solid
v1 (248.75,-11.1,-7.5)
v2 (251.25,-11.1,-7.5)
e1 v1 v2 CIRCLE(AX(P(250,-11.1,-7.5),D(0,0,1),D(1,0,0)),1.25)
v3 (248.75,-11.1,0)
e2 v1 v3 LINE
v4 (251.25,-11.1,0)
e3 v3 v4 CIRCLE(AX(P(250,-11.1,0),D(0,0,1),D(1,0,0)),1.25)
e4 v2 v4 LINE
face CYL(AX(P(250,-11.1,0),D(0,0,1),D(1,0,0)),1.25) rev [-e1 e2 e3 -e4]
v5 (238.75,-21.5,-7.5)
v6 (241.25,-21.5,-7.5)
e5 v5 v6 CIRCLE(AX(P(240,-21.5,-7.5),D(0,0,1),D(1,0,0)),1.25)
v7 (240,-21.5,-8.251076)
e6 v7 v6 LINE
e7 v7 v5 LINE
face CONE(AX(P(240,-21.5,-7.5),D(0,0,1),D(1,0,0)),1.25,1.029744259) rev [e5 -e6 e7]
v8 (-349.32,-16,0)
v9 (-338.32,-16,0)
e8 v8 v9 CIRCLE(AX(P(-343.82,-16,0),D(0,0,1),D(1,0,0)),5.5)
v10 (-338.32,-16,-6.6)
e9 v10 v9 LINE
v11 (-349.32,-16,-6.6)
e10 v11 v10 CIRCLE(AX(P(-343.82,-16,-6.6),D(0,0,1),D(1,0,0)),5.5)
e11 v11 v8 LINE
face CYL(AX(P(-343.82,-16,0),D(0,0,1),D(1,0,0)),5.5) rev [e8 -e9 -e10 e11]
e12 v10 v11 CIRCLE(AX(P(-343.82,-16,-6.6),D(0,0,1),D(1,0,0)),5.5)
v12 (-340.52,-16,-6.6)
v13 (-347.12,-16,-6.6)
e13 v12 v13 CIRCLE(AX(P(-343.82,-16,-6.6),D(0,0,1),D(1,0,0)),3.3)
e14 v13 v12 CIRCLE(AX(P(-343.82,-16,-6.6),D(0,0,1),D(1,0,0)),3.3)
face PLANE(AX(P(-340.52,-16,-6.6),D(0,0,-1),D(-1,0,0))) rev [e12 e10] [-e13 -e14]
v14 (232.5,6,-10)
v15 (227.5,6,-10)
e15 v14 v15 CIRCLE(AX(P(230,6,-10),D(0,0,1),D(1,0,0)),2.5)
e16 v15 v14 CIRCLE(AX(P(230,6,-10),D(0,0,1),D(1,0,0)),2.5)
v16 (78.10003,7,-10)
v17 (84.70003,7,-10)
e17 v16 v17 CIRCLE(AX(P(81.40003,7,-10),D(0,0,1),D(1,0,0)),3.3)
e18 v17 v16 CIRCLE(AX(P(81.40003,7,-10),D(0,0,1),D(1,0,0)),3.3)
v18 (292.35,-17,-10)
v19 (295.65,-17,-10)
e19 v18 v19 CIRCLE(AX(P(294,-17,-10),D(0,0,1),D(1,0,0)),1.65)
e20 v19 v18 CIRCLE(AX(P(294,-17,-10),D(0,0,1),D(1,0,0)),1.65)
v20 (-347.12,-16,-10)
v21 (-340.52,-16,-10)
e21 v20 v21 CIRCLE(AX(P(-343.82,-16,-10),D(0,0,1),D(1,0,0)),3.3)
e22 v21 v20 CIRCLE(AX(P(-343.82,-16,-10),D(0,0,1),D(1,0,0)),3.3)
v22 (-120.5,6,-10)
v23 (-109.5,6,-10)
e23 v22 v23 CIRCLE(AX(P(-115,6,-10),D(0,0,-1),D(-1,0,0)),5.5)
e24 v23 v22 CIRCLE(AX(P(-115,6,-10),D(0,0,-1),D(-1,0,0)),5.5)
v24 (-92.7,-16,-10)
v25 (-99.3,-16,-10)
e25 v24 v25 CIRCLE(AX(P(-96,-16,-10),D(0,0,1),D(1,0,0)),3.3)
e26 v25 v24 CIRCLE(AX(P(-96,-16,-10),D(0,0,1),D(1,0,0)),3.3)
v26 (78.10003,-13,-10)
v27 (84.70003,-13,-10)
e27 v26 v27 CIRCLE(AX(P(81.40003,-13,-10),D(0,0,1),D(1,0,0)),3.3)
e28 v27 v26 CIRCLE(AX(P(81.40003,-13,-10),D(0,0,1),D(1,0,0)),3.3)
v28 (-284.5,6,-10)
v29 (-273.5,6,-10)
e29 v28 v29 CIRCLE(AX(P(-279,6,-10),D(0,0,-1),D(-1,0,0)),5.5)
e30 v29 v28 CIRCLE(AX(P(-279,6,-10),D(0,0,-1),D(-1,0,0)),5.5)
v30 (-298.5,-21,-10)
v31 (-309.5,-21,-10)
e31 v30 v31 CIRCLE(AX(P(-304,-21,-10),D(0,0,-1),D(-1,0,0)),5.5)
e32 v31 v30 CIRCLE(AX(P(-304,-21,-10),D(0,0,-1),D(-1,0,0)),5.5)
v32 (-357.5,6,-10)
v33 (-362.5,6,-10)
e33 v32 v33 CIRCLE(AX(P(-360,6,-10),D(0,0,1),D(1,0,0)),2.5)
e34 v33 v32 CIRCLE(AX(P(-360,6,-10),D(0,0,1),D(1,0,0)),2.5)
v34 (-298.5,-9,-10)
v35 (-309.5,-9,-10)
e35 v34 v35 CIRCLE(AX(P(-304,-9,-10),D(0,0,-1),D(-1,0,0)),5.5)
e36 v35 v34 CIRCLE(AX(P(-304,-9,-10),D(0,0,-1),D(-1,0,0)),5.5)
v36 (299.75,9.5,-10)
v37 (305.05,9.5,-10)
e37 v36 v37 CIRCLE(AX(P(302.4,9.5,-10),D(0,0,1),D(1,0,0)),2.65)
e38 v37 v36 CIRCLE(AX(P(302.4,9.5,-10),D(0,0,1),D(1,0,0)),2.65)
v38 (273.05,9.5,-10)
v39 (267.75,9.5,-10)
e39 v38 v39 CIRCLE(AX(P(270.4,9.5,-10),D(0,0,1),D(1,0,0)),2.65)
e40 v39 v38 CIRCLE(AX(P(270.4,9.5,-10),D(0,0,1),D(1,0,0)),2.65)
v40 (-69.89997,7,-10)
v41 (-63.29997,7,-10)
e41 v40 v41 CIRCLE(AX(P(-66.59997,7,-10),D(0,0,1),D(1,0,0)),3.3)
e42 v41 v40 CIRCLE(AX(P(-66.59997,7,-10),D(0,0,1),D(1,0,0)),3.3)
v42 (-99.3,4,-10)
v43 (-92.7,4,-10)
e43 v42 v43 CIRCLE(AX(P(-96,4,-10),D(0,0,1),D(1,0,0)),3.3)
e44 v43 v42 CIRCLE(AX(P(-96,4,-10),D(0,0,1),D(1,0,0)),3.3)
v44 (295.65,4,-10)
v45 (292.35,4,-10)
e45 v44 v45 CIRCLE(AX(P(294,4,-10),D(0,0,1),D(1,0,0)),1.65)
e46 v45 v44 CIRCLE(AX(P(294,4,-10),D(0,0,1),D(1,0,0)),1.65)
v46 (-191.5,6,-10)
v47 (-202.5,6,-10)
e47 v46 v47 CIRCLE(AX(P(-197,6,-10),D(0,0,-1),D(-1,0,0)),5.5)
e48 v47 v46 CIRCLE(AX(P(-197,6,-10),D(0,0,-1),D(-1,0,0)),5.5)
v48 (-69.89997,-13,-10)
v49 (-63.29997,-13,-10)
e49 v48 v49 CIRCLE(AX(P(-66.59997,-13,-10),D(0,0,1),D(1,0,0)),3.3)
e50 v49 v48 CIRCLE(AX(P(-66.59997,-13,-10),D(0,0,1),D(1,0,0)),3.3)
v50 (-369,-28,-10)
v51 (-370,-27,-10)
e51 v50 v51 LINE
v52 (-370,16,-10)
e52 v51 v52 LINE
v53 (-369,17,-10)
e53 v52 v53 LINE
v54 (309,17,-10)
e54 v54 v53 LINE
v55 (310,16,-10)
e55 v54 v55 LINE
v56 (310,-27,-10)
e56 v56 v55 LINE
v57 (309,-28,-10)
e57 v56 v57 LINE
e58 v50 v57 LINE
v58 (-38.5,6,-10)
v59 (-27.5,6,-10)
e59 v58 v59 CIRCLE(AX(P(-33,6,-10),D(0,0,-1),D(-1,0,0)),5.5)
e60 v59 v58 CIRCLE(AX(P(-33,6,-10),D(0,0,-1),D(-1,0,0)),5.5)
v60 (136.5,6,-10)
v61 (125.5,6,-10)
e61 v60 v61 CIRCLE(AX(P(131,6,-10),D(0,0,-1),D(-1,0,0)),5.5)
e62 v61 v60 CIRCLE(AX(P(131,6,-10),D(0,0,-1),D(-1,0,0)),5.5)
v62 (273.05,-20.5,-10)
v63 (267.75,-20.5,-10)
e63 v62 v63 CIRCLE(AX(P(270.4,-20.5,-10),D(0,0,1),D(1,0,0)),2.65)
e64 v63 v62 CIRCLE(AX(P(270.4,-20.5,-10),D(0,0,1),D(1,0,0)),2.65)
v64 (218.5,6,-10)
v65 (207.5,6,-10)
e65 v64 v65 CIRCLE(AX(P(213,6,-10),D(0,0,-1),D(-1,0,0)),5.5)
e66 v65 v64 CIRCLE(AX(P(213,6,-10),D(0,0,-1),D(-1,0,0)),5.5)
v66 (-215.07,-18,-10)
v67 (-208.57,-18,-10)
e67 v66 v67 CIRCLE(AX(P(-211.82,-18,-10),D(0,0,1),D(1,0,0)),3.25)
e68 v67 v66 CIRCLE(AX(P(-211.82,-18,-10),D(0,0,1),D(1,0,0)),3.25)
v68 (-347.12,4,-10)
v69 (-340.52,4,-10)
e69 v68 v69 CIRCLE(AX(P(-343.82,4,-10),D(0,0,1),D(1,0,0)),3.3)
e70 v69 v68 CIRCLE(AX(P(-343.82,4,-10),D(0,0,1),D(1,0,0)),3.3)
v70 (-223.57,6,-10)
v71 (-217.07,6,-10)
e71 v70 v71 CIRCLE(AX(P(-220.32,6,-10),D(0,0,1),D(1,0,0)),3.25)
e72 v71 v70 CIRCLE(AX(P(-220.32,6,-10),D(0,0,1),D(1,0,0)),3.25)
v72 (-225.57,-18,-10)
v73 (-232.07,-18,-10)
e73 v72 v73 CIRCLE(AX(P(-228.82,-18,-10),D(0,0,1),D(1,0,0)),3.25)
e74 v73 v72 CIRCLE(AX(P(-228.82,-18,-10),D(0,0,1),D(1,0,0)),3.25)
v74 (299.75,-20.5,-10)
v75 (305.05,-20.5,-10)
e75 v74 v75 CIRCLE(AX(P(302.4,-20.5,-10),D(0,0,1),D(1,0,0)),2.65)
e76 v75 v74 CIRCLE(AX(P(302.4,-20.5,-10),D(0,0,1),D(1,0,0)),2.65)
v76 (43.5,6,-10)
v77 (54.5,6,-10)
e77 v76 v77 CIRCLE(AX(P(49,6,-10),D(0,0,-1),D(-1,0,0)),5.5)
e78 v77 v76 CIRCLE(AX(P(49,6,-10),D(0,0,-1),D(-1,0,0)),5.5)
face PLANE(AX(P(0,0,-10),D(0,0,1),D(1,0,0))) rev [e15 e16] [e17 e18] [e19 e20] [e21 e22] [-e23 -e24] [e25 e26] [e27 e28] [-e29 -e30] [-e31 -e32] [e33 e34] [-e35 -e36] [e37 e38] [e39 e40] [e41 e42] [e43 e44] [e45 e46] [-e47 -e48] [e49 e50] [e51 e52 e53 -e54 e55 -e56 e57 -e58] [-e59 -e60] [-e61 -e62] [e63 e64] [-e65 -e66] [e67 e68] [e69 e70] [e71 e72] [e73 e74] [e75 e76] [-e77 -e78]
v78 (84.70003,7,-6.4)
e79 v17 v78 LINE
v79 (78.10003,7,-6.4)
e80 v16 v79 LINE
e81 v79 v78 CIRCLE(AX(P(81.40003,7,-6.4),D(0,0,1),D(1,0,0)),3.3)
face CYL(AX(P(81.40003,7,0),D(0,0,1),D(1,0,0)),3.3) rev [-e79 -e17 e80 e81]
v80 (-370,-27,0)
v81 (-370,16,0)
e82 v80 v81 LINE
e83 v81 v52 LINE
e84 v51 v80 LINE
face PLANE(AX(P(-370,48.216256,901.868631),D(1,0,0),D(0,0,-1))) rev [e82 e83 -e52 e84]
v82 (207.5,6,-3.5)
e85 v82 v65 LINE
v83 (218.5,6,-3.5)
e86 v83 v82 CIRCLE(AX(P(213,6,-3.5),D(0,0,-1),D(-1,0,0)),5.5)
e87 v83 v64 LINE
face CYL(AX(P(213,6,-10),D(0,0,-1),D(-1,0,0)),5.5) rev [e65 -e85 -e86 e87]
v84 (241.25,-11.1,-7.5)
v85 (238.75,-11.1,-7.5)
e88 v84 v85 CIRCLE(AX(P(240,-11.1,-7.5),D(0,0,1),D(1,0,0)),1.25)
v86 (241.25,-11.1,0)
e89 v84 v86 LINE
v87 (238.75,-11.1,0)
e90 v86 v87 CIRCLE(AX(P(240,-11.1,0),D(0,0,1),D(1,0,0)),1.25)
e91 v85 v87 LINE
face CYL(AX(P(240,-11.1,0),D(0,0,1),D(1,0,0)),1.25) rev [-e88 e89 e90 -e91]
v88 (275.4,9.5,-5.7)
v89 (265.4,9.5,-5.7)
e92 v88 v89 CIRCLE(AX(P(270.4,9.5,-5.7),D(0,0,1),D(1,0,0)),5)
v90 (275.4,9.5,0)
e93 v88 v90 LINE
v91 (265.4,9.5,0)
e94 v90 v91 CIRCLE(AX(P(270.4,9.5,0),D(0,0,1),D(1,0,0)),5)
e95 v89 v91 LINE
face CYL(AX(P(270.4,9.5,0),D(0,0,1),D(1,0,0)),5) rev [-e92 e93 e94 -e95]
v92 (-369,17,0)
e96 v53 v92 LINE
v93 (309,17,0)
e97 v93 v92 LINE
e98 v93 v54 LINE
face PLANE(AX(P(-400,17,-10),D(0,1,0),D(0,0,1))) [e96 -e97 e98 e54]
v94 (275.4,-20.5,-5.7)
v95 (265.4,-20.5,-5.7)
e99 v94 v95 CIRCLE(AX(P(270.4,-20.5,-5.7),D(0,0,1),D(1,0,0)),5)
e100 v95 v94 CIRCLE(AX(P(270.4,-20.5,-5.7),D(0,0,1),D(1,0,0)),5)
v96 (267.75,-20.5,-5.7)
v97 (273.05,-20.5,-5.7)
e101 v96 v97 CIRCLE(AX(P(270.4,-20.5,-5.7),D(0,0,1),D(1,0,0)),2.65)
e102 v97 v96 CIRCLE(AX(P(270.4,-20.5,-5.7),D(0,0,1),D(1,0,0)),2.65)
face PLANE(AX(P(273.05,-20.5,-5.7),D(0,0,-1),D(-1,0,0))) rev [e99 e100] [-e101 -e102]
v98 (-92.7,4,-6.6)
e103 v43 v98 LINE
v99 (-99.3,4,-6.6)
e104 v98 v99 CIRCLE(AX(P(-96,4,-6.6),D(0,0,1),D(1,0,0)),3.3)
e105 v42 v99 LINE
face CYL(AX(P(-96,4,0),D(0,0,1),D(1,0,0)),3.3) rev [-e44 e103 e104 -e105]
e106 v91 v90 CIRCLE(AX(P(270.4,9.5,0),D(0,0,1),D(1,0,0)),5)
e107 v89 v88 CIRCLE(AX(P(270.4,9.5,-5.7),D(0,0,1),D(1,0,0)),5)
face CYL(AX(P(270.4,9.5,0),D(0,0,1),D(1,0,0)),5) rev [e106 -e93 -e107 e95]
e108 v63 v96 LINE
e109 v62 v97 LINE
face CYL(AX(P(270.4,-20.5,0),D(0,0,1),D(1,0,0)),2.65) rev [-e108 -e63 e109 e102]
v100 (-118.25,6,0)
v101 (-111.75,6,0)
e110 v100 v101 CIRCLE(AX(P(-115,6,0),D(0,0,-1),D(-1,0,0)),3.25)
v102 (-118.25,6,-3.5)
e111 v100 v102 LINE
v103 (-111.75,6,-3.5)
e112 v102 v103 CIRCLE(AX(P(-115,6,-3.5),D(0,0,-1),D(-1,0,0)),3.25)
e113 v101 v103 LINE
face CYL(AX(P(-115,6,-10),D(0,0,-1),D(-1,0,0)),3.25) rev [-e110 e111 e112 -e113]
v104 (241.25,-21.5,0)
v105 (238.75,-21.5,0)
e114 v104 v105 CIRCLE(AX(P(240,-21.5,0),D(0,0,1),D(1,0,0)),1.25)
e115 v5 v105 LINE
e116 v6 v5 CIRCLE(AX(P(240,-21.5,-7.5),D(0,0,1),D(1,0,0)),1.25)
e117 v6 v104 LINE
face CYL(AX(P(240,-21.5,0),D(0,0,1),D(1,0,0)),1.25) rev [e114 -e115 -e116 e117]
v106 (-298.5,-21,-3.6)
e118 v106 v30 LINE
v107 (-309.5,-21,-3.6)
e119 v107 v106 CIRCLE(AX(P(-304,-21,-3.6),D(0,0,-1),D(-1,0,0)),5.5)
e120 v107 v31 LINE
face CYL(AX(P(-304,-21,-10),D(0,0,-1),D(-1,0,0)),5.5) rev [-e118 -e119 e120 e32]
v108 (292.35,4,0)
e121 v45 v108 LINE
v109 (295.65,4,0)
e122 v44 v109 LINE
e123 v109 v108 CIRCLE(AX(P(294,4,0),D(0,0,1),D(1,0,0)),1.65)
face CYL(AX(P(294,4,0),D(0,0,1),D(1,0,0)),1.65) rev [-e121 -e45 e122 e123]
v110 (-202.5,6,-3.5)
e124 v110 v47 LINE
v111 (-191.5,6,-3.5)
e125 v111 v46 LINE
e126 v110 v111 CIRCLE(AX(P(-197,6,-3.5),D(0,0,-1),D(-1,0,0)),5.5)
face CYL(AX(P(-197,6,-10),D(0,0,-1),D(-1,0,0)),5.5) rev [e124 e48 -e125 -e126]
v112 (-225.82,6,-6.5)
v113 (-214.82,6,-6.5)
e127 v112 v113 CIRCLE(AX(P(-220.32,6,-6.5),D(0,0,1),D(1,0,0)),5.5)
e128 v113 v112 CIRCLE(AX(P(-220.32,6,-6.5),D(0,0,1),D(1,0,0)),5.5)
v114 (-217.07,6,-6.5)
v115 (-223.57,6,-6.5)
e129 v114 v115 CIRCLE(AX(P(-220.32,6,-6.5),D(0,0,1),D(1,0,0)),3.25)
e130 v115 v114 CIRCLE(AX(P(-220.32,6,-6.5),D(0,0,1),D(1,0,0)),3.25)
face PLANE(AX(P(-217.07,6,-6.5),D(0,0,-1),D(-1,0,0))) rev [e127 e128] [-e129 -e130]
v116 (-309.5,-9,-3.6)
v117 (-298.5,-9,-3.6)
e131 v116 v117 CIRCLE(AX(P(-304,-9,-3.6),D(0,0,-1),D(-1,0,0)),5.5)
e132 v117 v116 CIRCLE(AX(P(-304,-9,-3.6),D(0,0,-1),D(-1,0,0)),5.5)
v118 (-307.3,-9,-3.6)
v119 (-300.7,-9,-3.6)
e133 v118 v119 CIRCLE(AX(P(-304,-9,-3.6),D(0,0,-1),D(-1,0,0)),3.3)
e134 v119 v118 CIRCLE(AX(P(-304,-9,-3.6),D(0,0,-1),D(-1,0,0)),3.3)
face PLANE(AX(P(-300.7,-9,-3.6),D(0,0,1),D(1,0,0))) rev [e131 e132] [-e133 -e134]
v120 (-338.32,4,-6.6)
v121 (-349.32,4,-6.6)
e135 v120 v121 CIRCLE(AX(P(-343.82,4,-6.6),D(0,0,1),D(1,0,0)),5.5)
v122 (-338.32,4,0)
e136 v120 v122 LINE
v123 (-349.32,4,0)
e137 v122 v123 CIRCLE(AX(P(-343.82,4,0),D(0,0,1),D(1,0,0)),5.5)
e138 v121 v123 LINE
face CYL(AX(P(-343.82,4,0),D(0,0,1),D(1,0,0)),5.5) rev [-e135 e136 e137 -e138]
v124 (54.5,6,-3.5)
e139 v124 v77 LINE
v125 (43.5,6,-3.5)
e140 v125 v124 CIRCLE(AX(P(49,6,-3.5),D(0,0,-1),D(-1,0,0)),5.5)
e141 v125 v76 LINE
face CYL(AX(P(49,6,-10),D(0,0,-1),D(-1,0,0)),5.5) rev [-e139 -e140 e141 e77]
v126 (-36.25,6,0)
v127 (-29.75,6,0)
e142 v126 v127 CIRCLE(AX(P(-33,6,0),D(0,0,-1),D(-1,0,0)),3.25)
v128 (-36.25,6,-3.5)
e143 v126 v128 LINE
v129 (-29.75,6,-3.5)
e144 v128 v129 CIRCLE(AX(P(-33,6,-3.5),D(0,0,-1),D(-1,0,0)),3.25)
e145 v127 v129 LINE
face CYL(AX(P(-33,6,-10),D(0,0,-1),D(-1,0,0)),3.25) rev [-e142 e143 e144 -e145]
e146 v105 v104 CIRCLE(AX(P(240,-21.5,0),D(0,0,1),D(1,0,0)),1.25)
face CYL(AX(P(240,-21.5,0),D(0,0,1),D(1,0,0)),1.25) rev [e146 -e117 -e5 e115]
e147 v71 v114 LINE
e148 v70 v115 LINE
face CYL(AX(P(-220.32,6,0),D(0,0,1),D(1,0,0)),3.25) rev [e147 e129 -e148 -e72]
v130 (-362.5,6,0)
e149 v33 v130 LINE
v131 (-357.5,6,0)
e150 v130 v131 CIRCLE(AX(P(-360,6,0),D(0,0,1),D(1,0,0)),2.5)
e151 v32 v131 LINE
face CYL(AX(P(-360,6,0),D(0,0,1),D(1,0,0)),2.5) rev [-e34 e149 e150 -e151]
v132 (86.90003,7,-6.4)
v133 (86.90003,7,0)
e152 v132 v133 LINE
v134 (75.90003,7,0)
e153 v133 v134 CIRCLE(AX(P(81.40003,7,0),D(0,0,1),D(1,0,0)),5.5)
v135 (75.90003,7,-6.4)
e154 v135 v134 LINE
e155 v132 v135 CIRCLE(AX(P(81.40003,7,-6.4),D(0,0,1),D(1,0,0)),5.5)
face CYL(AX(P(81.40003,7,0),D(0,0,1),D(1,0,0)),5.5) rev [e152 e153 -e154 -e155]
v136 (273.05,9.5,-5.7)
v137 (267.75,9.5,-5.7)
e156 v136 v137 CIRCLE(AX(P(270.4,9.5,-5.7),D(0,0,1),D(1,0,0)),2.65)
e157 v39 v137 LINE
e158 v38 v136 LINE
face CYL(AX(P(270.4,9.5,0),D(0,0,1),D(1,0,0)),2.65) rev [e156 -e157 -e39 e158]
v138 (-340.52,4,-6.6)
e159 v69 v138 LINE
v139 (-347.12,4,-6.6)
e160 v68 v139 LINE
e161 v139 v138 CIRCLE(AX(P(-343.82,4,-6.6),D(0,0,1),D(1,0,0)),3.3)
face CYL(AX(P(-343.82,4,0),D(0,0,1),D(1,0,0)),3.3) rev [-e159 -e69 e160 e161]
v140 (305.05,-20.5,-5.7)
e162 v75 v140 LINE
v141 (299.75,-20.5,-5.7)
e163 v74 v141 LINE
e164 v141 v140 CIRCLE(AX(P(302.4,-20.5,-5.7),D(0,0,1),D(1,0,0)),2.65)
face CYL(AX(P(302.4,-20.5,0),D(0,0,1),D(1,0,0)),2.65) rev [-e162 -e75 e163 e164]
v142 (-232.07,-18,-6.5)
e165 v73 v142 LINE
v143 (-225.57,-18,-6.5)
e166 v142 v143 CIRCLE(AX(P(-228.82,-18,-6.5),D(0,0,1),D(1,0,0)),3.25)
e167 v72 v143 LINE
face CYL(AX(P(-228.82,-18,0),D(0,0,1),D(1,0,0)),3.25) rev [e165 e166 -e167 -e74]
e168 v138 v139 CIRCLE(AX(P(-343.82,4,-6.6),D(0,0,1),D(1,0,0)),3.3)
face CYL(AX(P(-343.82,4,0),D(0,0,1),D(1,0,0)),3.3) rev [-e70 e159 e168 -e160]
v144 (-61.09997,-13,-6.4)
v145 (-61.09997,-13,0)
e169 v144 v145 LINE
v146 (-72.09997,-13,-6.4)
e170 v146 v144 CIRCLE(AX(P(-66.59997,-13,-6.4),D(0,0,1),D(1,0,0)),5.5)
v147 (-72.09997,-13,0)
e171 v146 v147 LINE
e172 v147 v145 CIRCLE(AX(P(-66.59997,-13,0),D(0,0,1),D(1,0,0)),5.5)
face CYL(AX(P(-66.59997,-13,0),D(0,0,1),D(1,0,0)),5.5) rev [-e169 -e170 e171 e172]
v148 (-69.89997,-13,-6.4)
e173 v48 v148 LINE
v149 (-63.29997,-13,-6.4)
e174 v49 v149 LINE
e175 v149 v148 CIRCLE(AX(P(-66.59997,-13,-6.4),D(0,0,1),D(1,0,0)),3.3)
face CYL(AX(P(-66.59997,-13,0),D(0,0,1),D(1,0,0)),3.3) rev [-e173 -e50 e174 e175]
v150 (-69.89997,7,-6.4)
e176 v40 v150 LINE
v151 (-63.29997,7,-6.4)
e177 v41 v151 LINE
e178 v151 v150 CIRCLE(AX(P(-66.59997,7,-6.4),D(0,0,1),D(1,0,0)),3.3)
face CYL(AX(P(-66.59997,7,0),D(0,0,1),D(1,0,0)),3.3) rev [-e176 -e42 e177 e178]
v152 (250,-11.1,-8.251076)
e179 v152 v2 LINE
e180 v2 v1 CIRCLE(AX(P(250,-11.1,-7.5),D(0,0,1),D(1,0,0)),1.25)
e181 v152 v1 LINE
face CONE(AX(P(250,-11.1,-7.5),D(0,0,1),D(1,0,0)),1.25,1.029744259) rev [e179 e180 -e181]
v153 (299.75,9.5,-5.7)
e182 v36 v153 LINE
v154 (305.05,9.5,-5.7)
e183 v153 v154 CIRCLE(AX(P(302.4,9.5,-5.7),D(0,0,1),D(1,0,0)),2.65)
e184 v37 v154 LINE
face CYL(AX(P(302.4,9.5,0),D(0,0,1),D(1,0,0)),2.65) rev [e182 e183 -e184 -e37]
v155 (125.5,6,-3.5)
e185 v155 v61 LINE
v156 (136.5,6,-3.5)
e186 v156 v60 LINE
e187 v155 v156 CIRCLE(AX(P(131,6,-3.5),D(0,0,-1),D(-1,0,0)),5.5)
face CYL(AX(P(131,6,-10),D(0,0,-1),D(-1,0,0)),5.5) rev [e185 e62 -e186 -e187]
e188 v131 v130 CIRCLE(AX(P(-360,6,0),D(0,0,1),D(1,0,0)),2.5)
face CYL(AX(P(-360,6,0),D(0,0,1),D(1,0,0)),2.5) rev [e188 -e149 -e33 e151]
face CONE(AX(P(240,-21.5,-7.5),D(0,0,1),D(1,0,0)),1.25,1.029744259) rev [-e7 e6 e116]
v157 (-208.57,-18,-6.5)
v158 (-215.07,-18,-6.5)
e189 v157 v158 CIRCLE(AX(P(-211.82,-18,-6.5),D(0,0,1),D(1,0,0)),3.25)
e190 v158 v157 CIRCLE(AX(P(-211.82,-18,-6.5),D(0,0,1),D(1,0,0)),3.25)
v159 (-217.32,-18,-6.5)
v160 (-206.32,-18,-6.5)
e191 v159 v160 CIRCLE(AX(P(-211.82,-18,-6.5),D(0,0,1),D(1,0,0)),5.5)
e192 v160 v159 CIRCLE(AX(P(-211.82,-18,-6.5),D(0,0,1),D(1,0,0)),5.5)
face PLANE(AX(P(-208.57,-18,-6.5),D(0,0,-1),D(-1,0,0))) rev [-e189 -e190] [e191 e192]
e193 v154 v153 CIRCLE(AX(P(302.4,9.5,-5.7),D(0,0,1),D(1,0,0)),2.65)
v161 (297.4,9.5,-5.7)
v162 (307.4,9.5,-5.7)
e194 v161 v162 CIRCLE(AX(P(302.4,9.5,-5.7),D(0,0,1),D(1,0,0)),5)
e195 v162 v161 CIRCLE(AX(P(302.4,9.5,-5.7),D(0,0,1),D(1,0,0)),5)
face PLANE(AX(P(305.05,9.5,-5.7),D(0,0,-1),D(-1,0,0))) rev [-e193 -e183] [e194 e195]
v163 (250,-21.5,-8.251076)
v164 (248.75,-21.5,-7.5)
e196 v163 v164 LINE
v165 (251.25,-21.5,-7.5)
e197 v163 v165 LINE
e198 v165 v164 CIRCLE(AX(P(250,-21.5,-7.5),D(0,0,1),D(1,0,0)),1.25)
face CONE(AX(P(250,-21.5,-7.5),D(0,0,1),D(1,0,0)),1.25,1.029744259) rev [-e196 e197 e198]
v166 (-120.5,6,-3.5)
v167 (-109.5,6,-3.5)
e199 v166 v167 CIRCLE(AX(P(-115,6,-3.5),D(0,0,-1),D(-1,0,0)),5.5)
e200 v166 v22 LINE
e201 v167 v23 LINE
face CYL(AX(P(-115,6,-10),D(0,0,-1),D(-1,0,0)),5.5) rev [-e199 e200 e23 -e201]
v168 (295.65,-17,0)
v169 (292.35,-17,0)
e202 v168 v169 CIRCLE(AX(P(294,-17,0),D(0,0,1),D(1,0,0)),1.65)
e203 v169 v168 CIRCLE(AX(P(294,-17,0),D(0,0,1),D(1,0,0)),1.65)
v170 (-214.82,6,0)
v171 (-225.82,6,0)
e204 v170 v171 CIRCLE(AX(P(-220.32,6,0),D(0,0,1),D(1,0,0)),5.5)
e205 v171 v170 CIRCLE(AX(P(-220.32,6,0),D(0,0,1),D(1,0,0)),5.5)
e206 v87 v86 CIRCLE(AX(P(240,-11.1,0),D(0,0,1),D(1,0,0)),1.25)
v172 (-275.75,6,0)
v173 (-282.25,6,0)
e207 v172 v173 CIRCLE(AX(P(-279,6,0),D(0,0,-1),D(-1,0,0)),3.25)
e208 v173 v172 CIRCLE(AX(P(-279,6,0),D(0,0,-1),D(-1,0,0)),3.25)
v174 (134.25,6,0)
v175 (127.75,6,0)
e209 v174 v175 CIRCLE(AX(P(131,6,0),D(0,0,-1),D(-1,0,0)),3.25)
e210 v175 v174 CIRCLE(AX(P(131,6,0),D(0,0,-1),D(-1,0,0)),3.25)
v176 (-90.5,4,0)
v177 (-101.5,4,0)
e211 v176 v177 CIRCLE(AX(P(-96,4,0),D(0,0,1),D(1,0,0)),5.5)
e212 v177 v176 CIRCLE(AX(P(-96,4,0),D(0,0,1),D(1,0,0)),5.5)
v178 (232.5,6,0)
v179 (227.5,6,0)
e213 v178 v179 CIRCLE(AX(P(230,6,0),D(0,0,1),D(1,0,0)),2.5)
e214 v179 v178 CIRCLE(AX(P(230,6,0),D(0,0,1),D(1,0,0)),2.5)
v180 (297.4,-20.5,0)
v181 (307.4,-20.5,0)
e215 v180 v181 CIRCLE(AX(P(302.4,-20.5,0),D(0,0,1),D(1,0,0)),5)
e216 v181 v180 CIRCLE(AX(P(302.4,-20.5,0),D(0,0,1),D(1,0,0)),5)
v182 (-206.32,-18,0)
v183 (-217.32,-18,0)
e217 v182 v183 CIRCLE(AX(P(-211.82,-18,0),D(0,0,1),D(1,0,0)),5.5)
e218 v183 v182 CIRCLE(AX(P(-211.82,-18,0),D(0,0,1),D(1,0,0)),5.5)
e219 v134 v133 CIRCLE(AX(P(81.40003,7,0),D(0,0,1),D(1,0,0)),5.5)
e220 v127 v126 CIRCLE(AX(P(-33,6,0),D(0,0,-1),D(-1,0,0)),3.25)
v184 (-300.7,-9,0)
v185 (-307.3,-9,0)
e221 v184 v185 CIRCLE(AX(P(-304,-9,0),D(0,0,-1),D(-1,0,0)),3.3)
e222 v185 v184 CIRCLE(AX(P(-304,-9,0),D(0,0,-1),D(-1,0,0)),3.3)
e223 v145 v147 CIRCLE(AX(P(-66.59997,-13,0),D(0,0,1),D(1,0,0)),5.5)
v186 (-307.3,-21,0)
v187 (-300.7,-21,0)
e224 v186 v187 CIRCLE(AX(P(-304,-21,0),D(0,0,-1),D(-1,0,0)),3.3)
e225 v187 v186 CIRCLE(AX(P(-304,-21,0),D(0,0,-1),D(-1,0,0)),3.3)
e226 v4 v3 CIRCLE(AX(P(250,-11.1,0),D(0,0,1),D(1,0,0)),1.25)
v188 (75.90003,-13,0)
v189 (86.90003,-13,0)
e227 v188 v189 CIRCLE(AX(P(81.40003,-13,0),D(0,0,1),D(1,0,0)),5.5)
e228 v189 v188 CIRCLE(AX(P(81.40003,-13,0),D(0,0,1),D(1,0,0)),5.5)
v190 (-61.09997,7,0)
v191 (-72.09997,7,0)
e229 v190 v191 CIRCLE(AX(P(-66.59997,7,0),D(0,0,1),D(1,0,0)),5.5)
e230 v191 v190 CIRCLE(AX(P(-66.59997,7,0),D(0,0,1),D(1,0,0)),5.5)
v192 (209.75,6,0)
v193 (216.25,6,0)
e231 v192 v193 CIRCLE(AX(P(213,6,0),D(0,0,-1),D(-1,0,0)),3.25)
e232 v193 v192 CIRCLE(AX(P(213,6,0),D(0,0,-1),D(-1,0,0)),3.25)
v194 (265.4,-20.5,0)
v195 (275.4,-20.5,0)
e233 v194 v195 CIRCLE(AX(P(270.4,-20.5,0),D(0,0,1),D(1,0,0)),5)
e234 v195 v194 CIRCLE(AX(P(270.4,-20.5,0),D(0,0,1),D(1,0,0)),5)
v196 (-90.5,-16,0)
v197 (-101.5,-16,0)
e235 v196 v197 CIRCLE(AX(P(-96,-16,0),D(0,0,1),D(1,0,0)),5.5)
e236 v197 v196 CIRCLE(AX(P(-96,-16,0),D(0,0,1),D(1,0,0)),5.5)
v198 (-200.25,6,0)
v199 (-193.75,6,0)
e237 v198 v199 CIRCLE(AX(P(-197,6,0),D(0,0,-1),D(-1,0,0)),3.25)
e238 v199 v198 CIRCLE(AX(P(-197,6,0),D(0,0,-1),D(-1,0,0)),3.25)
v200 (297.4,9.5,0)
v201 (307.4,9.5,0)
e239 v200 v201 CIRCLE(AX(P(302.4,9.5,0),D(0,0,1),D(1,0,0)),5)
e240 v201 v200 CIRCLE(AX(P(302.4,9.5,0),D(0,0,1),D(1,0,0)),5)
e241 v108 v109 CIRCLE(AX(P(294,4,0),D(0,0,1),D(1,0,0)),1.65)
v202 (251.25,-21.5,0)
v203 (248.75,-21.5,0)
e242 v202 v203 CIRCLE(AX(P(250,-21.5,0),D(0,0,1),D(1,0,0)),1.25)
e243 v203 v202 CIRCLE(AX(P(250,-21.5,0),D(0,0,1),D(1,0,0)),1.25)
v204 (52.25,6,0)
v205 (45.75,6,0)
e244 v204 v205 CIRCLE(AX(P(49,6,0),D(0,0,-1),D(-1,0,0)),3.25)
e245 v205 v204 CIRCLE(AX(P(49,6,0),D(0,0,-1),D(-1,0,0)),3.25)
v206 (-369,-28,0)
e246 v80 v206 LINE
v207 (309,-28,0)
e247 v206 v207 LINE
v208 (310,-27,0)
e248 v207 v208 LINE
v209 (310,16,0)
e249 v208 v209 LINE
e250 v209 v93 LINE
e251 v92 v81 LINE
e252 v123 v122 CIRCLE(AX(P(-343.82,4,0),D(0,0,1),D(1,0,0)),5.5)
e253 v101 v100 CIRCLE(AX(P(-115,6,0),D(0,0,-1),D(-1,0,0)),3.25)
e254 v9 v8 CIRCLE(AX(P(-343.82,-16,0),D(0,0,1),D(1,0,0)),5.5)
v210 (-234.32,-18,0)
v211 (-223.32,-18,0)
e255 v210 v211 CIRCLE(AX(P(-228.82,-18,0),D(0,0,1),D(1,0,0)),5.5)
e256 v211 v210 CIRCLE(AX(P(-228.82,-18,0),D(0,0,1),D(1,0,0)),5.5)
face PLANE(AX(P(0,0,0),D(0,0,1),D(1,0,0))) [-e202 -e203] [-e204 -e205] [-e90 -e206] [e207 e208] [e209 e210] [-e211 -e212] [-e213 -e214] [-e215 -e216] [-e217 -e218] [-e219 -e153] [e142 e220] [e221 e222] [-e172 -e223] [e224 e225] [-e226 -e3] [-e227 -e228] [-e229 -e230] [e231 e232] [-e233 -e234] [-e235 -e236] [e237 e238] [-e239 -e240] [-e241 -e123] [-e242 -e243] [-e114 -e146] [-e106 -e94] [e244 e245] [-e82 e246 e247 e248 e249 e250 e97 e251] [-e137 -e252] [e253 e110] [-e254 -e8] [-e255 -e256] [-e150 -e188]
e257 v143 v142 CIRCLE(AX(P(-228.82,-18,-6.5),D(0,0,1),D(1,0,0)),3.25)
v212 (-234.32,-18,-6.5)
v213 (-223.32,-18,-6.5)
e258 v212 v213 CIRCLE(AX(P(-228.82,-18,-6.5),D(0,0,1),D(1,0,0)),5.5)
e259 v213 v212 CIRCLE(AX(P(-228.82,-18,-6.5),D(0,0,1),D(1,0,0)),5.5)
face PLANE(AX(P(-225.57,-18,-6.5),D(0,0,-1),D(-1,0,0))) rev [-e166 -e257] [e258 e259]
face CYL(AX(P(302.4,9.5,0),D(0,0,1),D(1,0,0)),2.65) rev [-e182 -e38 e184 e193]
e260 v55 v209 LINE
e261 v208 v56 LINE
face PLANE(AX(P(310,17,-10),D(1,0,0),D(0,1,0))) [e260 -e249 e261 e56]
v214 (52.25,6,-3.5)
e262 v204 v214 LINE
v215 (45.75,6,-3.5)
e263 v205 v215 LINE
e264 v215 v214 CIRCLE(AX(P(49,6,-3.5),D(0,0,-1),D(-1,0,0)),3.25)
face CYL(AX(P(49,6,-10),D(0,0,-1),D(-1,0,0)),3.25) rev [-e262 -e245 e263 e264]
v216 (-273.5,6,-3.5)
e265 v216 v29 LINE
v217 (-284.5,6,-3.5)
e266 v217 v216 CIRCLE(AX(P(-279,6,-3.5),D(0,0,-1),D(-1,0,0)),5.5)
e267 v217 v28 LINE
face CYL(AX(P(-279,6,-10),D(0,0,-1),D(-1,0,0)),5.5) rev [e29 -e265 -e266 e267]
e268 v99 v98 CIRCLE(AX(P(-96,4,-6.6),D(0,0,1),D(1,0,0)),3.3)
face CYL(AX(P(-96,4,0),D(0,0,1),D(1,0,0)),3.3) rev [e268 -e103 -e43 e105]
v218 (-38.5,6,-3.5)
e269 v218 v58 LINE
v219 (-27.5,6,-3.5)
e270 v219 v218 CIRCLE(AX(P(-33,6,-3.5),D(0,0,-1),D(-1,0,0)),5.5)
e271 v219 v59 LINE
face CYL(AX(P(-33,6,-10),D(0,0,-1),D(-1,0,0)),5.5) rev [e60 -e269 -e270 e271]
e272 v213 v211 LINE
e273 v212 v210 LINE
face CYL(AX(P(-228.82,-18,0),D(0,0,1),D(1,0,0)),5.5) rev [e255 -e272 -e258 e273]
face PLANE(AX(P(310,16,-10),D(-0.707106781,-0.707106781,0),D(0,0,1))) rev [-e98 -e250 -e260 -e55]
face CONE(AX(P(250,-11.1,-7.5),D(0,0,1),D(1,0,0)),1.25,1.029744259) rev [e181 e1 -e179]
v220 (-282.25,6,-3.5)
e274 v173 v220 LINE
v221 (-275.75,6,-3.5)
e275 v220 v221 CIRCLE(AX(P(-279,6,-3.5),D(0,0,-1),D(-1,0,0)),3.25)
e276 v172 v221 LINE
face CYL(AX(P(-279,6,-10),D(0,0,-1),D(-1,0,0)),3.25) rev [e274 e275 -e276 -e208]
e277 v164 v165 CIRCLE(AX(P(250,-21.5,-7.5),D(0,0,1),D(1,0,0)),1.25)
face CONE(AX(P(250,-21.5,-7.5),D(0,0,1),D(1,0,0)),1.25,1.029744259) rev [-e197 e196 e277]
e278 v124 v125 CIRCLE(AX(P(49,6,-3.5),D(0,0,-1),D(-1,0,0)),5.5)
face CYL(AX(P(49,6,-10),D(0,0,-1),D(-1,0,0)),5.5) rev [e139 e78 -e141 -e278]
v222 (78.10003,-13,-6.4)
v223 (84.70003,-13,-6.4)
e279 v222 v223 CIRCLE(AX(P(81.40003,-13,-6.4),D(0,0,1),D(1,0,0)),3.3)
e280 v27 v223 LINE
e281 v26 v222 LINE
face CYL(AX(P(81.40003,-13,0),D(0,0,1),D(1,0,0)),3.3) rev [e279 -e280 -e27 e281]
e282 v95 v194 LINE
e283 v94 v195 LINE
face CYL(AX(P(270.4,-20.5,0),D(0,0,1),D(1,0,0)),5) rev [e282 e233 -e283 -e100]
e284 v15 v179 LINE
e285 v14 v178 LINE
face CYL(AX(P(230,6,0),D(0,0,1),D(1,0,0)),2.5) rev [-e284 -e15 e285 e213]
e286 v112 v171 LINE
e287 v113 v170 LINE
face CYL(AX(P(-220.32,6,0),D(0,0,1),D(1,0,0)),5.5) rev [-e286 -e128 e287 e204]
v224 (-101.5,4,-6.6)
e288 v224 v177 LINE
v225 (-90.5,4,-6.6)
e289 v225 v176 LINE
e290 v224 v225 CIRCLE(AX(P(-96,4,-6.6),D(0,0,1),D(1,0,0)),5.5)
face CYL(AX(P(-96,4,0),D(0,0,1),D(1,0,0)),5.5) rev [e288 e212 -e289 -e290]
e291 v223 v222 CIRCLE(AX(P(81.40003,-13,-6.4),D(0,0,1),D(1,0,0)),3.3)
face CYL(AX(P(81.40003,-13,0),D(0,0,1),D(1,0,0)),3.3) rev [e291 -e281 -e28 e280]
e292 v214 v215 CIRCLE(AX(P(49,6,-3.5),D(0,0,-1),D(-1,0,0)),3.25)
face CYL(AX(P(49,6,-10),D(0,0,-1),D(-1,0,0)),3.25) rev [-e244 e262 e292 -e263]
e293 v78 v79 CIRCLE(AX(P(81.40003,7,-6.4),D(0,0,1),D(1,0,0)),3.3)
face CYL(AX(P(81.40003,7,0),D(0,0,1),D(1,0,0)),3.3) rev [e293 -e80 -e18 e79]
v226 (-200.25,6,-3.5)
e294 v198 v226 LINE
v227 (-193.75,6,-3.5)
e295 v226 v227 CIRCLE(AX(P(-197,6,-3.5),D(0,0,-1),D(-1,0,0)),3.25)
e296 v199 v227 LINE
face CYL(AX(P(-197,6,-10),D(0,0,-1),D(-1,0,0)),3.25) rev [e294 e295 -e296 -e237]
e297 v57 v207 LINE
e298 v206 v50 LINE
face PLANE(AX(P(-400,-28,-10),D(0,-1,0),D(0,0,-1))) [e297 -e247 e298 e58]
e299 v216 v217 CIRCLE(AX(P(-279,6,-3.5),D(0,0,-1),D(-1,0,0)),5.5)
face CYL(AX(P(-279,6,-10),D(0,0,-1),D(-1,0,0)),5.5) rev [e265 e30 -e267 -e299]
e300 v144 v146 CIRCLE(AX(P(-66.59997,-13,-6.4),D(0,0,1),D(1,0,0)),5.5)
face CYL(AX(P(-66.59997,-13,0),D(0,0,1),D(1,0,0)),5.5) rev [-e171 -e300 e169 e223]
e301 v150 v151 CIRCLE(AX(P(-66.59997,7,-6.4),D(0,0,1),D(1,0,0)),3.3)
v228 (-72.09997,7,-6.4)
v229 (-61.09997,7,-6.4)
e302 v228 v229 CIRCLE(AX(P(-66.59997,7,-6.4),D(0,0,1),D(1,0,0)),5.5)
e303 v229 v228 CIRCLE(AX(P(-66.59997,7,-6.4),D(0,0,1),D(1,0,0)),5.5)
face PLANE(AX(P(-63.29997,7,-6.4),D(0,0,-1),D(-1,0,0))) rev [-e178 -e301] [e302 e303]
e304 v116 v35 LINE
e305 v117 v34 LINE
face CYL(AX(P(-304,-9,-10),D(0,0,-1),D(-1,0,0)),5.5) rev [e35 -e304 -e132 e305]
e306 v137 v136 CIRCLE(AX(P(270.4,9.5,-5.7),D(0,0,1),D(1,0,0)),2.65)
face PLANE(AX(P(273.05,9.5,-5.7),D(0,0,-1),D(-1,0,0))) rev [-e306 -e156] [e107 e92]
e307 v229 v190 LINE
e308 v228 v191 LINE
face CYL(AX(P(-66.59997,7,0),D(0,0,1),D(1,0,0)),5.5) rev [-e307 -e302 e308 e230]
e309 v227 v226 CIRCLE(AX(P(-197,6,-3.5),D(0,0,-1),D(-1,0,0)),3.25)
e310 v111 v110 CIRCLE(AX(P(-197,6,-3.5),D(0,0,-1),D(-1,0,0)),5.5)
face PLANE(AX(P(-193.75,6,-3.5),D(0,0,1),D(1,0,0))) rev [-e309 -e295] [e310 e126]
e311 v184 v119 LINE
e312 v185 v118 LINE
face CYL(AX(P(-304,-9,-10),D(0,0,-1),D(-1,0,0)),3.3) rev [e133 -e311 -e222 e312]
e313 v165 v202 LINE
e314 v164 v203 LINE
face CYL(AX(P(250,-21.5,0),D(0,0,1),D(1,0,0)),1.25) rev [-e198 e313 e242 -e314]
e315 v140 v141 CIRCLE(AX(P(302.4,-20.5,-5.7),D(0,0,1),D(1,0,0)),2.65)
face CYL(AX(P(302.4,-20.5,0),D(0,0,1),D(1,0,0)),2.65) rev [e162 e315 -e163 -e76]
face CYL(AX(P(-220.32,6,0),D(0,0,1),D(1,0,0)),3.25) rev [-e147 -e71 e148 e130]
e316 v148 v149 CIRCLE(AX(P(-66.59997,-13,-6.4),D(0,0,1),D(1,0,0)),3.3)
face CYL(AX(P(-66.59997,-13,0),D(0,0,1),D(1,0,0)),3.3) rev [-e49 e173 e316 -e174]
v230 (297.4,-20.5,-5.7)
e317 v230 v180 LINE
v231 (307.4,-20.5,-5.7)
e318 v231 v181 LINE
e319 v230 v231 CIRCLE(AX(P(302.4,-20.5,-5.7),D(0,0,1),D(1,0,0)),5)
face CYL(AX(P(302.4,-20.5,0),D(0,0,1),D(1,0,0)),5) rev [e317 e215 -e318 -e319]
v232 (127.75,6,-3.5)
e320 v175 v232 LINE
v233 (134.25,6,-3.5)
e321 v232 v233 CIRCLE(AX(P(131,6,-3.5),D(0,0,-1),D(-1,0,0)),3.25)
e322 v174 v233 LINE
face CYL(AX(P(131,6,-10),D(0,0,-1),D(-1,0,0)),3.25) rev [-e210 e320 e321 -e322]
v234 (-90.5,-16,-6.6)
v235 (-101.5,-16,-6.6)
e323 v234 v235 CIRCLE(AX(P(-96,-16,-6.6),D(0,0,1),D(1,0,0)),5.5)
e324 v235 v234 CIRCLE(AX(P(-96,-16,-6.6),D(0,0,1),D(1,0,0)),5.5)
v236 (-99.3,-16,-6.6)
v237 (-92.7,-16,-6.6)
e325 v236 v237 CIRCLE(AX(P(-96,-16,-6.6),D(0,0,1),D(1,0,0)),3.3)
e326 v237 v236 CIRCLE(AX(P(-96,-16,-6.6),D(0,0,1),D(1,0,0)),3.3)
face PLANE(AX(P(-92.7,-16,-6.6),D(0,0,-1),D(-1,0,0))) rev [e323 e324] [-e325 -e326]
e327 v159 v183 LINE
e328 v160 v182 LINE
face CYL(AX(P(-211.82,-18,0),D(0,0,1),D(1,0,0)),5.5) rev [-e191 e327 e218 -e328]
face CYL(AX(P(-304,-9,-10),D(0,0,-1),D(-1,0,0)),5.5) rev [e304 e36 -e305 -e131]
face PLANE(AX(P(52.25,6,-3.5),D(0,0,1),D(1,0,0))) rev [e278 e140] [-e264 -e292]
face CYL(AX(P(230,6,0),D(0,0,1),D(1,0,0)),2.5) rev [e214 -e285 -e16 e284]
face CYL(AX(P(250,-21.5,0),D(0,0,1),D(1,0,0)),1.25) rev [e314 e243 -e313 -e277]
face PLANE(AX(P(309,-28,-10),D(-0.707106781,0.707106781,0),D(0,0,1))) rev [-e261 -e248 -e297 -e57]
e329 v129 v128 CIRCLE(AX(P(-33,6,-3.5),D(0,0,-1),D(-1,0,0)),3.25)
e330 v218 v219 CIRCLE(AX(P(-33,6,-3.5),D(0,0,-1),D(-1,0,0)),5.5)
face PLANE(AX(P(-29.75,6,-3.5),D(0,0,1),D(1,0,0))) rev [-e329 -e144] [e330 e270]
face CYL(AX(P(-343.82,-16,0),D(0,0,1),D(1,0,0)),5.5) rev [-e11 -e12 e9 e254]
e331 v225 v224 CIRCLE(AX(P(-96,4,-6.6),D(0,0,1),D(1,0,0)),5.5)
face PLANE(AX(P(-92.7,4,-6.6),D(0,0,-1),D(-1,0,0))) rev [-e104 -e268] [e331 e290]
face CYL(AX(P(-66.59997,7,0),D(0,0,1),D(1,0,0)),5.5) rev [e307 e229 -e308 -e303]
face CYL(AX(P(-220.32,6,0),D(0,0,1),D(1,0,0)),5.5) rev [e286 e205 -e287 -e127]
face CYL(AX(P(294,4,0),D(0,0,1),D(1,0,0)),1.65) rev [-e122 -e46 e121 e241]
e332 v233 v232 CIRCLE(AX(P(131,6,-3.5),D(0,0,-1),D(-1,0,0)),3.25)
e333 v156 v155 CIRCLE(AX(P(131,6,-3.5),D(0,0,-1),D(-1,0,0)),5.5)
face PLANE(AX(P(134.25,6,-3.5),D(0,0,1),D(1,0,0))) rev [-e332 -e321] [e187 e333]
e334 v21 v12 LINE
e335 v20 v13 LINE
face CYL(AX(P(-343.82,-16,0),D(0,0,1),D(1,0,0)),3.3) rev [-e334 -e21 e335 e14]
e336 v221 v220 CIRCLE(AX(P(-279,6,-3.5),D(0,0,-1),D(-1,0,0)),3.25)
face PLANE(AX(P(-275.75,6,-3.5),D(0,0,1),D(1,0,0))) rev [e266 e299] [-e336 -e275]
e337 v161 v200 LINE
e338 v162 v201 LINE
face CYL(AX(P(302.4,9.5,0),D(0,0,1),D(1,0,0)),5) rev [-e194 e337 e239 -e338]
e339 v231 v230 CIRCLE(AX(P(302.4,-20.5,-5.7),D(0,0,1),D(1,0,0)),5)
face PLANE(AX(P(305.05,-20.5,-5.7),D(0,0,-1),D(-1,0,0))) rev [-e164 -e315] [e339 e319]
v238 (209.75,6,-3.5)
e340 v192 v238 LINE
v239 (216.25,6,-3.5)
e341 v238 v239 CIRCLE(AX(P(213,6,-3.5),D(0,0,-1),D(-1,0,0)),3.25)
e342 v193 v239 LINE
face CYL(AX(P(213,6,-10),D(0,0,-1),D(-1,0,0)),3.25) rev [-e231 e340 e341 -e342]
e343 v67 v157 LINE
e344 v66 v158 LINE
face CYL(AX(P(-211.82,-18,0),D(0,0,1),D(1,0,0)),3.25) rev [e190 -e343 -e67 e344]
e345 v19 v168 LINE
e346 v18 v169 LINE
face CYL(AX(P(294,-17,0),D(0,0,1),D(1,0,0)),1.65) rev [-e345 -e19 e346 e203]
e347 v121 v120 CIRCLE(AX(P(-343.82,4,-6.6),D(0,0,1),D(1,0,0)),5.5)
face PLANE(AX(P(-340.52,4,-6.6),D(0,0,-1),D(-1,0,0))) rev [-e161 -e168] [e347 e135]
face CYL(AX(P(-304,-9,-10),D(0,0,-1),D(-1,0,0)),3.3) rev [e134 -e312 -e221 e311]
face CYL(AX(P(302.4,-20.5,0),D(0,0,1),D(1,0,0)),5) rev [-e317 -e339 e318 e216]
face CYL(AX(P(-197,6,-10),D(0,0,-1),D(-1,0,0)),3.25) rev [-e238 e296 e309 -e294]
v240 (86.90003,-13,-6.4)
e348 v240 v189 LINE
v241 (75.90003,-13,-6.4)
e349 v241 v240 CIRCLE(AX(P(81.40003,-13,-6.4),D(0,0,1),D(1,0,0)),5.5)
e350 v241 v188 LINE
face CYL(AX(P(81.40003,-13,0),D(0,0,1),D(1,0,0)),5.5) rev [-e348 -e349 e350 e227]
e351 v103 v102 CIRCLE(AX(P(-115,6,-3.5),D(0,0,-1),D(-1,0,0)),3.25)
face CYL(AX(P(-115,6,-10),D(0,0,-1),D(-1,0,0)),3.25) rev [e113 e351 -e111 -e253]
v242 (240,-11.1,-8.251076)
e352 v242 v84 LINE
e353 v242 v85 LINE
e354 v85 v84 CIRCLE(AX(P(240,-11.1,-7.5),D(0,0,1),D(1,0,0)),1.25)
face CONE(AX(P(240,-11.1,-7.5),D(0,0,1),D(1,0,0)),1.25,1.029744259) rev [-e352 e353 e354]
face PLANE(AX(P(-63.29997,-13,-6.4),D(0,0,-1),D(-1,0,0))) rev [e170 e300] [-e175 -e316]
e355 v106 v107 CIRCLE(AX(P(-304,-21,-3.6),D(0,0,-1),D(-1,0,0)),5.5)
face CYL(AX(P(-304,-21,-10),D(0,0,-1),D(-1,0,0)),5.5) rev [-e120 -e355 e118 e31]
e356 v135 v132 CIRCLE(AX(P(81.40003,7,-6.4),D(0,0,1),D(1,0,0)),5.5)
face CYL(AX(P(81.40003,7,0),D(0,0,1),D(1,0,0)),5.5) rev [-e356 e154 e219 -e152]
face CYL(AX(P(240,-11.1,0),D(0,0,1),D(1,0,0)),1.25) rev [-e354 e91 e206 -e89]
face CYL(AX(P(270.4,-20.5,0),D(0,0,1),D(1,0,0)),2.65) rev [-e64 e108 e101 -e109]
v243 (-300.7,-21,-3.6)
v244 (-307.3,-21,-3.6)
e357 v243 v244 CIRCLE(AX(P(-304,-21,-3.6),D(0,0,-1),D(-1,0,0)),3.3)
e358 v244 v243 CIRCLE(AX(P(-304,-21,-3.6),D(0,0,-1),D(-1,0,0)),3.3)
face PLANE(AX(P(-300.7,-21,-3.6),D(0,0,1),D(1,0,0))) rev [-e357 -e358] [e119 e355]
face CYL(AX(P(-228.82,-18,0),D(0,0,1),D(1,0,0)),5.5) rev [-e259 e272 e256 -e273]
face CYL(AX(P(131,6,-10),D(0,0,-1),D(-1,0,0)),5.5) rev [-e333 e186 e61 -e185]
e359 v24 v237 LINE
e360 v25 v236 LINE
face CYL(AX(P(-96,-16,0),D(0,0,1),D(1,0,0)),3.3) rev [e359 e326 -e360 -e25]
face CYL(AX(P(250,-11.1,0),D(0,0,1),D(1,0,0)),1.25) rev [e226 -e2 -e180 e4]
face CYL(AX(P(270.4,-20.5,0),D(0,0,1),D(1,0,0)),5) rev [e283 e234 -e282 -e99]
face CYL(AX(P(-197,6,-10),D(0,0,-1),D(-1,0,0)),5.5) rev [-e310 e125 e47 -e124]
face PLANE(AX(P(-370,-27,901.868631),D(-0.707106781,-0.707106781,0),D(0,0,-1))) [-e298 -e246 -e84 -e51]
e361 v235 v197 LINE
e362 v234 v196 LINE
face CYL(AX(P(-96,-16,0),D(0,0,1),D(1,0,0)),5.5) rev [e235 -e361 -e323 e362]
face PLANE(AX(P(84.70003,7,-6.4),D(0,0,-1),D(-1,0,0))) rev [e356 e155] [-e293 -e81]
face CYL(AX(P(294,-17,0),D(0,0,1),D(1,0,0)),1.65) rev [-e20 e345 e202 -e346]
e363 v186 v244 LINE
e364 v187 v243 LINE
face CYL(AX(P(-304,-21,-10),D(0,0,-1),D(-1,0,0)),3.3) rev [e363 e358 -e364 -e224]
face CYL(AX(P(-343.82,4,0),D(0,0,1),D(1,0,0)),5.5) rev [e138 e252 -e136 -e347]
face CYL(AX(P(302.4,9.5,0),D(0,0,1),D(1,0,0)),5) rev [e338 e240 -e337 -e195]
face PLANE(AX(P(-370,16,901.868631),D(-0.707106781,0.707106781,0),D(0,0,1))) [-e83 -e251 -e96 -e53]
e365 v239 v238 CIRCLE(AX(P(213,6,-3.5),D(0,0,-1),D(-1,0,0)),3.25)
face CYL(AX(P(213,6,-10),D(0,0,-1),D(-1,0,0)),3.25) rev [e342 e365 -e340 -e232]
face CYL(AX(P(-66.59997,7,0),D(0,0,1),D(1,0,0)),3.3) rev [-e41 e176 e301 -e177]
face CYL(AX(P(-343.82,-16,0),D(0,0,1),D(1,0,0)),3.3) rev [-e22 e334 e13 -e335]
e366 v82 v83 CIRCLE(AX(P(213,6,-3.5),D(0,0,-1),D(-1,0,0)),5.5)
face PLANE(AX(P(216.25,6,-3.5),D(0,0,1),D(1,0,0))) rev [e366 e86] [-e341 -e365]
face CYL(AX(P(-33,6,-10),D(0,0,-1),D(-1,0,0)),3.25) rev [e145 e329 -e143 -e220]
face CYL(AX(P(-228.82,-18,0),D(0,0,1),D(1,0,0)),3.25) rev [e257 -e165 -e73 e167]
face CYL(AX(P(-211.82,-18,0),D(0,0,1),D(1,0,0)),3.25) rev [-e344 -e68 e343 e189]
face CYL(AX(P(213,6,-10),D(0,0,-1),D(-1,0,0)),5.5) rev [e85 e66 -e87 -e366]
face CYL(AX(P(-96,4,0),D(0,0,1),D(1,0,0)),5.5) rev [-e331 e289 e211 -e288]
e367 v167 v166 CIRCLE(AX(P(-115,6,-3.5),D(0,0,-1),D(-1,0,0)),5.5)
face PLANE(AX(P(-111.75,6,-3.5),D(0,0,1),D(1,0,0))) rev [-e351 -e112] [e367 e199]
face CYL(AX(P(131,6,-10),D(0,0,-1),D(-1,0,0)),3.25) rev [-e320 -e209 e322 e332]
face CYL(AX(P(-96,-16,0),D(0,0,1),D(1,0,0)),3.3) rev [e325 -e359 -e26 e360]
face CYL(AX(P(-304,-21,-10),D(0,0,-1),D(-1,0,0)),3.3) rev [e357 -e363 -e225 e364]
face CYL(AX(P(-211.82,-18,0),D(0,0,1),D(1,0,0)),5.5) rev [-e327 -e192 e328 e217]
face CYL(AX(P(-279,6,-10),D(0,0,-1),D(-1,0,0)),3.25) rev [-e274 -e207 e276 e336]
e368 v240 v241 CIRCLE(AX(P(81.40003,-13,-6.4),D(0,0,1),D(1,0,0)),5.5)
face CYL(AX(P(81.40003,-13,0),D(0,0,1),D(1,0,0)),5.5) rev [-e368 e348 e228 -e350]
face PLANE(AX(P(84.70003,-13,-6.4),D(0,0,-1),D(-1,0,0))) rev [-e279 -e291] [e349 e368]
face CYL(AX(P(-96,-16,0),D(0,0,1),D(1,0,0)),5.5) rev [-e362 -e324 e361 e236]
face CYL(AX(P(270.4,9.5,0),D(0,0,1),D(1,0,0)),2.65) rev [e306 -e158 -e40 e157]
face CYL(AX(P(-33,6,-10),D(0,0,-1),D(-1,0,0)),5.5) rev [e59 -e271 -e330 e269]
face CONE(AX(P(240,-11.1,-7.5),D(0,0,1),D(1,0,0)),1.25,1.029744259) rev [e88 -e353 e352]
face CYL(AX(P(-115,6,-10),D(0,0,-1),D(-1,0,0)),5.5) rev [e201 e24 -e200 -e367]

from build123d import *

# Parameters (mm, degrees)
SKETCH_1_W                    = 710
SKETCH_1_H                    = 45
EXTRUDE_1_DEPTH               = 10
HOLE_WIZARD_C_2_D             = 6.5
HOLE_WIZARD_C_2_CBORE_D       = 11
HOLE_WIZARD_C_2_CBORE_DEPTH   = 6.5
PATTERN_LINEAR_1_COUNT        = 7
PATTERN_LINEAR_1_PITCH        = 82
HOLE_WIZARD_C_1_D             = 6.6
HOLE_WIZARD_C_1_CBORE_D       = 11
HOLE_WIZARD_C_1_CBORE_DEPTH   = 6.6
HOLE_WIZARD_C_2_2_D           = 6.6
HOLE_WIZARD_C_2_2_CBORE_D     = 11
HOLE_WIZARD_C_2_2_CBORE_DEPTH = 6.6
HOLE_WIZARD_C_3_D             = 6.5
HOLE_WIZARD_C_3_CBORE_D       = 11
HOLE_WIZARD_C_3_CBORE_DEPTH   = 6.5
HOLE_WIZARD_M6_1_D            = 6.6
HOLE_WIZARD_M6_1_CBORE_D      = 11
HOLE_WIZARD_M6_1_CBORE_DEPTH  = 6.4
HOLE_WIZARD_M6_2_D            = 6.6
HOLE_WIZARD_M6_2_CBORE_D      = 11
HOLE_WIZARD_M6_2_CBORE_DEPTH  = 6.4
CHAMFER_1_SIZE                = 1
HOLE_WIZARD_5_0_5_1_D         = 5
HOLE_WIZARD_5_0_5_1_DEPTH     = 15.61
HOLE_WIZARD_5_0_5_1_TIP       = 1.443375673
HOLE_WIZARD_1_D               = 5.3
HOLE_WIZARD_1_CBORE_D         = 10
HOLE_WIZARD_1_CBORE_DEPTH     = 5.7
HOLE_WIZARD_M4_1_D            = 3.3
HOLE_WIZARD_M4_1_DEPTH        = 10.1
HOLE_WIZARD_M4_1_TIP          = 0.991420021
CUT_EXTRUDE_1_DEPTH           = 402.103477921
CUT_EXTRUDE_1_DEPTH_BACK      = 402.103477921
CHAMFER_2_SIZE                = 1
HOLE_WIZARD_M3_1_D            = 2.5
HOLE_WIZARD_M3_1_DEPTH        = 7.5
HOLE_WIZARD_M3_1_TIP          = 0.751075774


with BuildPart() as part:
    # 草图1 → 凸台-拉伸1 (new body)
    with BuildSketch(Plane.XY):
        with Locations((-45, -5.5)):
            Rectangle(SKETCH_1_W, SKETCH_1_H)
    extrude(amount=-EXTRUDE_1_DEPTH)

    # Hole Wizard C _2 (through all)
    with Locations(Plane(origin=(0, 0, -10), x_dir=(-1, 0, 0), z_dir=(0, 0, -1))):
        with Locations((-213, 6)):
            hole_wizard_c_2 = CounterBoreHole(HOLE_WIZARD_C_2_D / 2, HOLE_WIZARD_C_2_CBORE_D / 2, HOLE_WIZARD_C_2_CBORE_DEPTH)

    # 阵列(线性)1: Hole Wizard C _2 ×7
    with Locations(*[(-i * PATTERN_LINEAR_1_PITCH, 0, 0) for i in range(1, PATTERN_LINEAR_1_COUNT)]):
        add(hole_wizard_c_2, mode=Mode.SUBTRACT)

    # 打孔尺寸根据六角头螺栓 C 级的类型1 (through all)
    with Locations(Plane.XY):
        with Locations((-343.82, -16), (-343.82, 4)):
            CounterBoreHole(HOLE_WIZARD_C_1_D / 2, HOLE_WIZARD_C_1_CBORE_D / 2, HOLE_WIZARD_C_1_CBORE_DEPTH)

    # Hole Wizard C _2 2 (through all)
    with Locations(Plane.XY):
        with Locations((-96, -16), (-96, 4)):
            CounterBoreHole(HOLE_WIZARD_C_2_2_D / 2, HOLE_WIZARD_C_2_2_CBORE_D / 2, HOLE_WIZARD_C_2_2_CBORE_DEPTH)

    # 打孔尺寸根据六角头螺栓 C 级的类型3 (through all)
    with Locations(Plane.XY):
        with Locations((-228.82, -18), (-211.82, -18), (-220.32, 6)):
            CounterBoreHole(HOLE_WIZARD_C_3_D / 2, HOLE_WIZARD_C_3_CBORE_D / 2, HOLE_WIZARD_C_3_CBORE_DEPTH)

    # M6 六角凹头螺钉的柱形沉头孔1 (through all)
    with Locations(Plane(origin=(0, 0, -10), x_dir=(-1, 0, 0), z_dir=(0, 0, -1))):
        with Locations((304, -21), (304, -9)):
            CounterBoreHole(HOLE_WIZARD_M6_1_D / 2, HOLE_WIZARD_M6_1_CBORE_D / 2, HOLE_WIZARD_M6_1_CBORE_DEPTH)

    # M6 六角凹头螺钉的柱形沉头孔2 (through all)
    with Locations(Plane.XY):
        with Locations((81.400029989, 7), (81.400029989, -13), (-66.599970011, 7), (-66.599970011, -13)):
            CounterBoreHole(HOLE_WIZARD_M6_2_D / 2, HOLE_WIZARD_M6_2_CBORE_D / 2, HOLE_WIZARD_M6_2_CBORE_DEPTH)

    # 倒角1
    chamfer_1_edges = [part.edges().sort_by_distance(p)[0] for p in [
        (-400, 17, -5),
        (310, 17, -5),
        (310, -28, -5),
        (-400, -28, -5),
    ]]
    chamfer(chamfer_1_edges, length=CHAMFER_1_SIZE)

    # Ø5.0 (5) 直径孔1
    with Locations(Plane.XY):
        with Locations((230, 6), (-360, 6)):
            Hole(HOLE_WIZARD_5_0_5_1_D / 2, depth=HOLE_WIZARD_5_0_5_1_DEPTH)
            with Locations((0, 0, -(HOLE_WIZARD_5_0_5_1_DEPTH + HOLE_WIZARD_5_0_5_1_TIP / 2))):  # 120° drill point
                Cone(0, HOLE_WIZARD_5_0_5_1_D / 2, HOLE_WIZARD_5_0_5_1_TIP, mode=Mode.SUBTRACT)

    # 打孔尺寸根据内六角圆柱头螺钉的类型1 (through all)
    with Locations(Plane.XY):
        with Locations((270.4, 9.5), (302.4, 9.5), (270.4, -20.5), (302.4, -20.5)):
            CounterBoreHole(HOLE_WIZARD_1_D / 2, HOLE_WIZARD_1_CBORE_D / 2, HOLE_WIZARD_1_CBORE_DEPTH)

    # M4 螺纹孔1
    with Locations(Plane.XY):
        with Locations((294, 4), (294, -17)):
            Hole(HOLE_WIZARD_M4_1_D / 2, depth=HOLE_WIZARD_M4_1_DEPTH)
            with Locations((0, 0, -(HOLE_WIZARD_M4_1_DEPTH + HOLE_WIZARD_M4_1_TIP / 2))):  # 118° drill point
                Cone(0, HOLE_WIZARD_M4_1_D / 2, HOLE_WIZARD_M4_1_TIP, mode=Mode.SUBTRACT)

    # 草图21 → 切除-拉伸1 (cut, two sides: drawn at the far end of the back side and taken through both)
    with BuildSketch(Plane.XY.offset(-CUT_EXTRUDE_1_DEPTH_BACK)):
        Polygon((-370, 1426.732120581), (-370, 48.216256267), (-370, -32.871094122), (-370, -1411.386958436), (-3127.031728627, -1411.386958436), (-3127.031728627, 1426.732120581), align=None)
    extrude(amount=CUT_EXTRUDE_1_DEPTH + CUT_EXTRUDE_1_DEPTH_BACK, mode=Mode.SUBTRACT)

    # 倒角2
    chamfer_2_edges = [part.edges().sort_by_distance(p)[0] for p in [
        (-370, -28, -5),
        (-370, 17, -5),
    ]]
    chamfer(chamfer_2_edges, length=CHAMFER_2_SIZE)

    # M3 螺纹孔1
    with Locations(Plane.XY):
        with Locations((240, -21.5), (240, -11.1), (250, -11.1), (250, -21.5)):
            Hole(HOLE_WIZARD_M3_1_D / 2, depth=HOLE_WIZARD_M3_1_DEPTH)
            with Locations((0, 0, -(HOLE_WIZARD_M3_1_DEPTH + HOLE_WIZARD_M3_1_TIP / 2))):  # 118° drill point
                Cone(0, HOLE_WIZARD_M3_1_D / 2, HOLE_WIZARD_M3_1_TIP, mode=Mode.SUBTRACT)


solid = part.part
